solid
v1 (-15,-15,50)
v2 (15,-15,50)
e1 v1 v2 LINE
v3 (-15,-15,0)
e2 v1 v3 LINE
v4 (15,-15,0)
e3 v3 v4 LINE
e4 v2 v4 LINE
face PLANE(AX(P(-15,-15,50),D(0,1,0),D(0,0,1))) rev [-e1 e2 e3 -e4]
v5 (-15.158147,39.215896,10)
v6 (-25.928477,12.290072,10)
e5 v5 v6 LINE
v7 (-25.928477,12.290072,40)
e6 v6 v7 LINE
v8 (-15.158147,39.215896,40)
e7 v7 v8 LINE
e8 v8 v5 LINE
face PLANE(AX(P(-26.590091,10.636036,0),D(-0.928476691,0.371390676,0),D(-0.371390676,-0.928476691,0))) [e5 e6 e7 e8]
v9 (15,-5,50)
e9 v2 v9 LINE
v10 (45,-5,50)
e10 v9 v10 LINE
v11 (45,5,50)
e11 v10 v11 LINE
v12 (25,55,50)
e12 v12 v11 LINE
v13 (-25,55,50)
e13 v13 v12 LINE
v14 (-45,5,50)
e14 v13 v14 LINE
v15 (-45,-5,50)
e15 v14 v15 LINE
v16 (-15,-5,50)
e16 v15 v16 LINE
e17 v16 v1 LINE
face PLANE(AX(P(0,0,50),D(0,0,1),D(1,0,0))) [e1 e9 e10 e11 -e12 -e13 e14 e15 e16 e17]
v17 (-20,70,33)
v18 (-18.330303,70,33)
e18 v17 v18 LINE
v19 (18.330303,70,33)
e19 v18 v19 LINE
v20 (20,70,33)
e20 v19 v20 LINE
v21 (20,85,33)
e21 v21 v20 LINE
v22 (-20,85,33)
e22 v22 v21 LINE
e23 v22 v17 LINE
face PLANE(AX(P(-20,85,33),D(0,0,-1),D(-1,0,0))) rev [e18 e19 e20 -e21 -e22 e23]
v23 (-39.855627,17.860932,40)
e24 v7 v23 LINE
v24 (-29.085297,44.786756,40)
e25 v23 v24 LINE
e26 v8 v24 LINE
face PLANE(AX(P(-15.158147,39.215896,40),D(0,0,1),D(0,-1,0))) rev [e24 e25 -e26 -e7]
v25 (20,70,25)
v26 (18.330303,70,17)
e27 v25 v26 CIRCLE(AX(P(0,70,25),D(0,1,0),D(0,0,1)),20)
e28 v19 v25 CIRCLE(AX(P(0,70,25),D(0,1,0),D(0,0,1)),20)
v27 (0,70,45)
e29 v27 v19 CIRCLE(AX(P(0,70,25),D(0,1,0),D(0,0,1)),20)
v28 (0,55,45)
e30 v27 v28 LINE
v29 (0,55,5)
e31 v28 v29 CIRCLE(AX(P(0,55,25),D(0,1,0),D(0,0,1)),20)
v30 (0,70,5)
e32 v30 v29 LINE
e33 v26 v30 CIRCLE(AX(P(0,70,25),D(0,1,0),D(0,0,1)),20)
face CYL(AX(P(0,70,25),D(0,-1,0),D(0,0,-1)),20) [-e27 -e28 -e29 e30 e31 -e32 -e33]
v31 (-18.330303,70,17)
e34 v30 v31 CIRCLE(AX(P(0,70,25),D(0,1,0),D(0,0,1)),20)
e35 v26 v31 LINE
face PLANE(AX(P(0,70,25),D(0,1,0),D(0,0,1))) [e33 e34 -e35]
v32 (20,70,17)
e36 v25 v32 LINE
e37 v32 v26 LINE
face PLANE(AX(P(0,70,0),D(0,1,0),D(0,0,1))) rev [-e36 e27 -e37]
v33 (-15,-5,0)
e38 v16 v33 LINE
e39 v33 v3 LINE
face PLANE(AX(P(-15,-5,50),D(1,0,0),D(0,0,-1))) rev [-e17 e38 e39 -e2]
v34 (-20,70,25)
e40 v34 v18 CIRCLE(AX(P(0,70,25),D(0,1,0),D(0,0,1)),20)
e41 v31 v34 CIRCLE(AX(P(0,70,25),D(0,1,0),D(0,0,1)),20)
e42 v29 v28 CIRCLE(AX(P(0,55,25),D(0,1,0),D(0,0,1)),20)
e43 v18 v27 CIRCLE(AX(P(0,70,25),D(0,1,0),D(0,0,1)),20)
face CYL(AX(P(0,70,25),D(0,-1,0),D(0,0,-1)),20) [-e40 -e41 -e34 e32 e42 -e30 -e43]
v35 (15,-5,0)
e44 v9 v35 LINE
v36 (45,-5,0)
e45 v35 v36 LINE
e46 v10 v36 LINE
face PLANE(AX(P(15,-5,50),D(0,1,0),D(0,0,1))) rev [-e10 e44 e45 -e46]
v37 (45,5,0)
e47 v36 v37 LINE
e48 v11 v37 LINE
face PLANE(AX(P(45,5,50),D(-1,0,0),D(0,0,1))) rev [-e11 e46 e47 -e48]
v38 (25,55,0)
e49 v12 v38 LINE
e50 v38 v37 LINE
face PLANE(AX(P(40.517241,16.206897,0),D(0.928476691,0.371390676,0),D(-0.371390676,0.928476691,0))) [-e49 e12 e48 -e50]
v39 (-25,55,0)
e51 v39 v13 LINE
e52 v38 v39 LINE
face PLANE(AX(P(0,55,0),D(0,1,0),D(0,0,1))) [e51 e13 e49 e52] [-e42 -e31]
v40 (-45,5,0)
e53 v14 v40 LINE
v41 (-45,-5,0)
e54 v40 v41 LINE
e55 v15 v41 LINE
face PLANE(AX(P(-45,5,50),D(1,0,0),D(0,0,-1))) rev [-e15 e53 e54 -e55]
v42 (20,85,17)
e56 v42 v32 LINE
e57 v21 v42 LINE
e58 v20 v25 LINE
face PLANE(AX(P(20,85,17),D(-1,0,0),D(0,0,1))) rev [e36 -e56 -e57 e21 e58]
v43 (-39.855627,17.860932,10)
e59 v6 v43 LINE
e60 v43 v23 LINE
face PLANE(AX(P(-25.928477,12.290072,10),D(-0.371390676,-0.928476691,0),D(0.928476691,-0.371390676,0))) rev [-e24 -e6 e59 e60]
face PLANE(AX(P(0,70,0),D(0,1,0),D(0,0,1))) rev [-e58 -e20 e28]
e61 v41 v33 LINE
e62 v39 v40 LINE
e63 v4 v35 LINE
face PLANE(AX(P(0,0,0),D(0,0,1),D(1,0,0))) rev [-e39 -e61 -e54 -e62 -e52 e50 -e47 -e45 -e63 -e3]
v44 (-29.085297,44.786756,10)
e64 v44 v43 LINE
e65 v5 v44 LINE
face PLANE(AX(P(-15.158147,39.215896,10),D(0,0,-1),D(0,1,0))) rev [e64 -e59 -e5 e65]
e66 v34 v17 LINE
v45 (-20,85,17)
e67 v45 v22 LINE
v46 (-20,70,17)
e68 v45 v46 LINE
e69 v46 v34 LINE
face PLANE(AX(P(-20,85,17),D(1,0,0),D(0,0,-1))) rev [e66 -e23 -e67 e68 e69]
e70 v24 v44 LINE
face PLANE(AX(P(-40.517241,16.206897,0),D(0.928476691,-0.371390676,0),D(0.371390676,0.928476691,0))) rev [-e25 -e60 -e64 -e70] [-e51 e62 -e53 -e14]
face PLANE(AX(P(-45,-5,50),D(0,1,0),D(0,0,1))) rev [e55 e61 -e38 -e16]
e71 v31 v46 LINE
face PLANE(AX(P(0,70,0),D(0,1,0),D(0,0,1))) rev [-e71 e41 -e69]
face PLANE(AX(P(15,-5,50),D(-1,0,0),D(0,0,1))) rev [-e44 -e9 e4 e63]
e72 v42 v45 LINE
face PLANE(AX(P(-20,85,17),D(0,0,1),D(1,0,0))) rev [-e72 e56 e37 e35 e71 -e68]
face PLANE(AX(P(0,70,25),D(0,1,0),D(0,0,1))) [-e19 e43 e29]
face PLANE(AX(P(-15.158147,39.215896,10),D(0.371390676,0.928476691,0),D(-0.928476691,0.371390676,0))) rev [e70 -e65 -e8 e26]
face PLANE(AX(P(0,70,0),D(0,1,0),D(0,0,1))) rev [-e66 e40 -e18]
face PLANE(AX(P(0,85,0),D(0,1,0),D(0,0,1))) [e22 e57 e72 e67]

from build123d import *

# Parameters (mm, degrees)
BASE_BLOCK_DEPTH    = 50
ROUND_BOSS_SKETCH_R = 20
ROUND_BOSS_DEPTH    = 15
TOP_KEY_SKETCH_W    = 40
TOP_KEY_SKETCH_H    = 16
TOP_KEY_DEPTH       = 15
SLOT_SKETCH_W       = 30
SLOT_SKETCH_H       = 29
SLOT_CUT_DEPTH      = 15


with BuildPart() as part:
    # Base Profile Sketch → Base Block (new body)
    with BuildSketch(Plane.XY):
        Polygon((15, -5), (45, -5), (45, 5), (-45, 5), (-45, -5), (-15, -5), (-15, -15), (15, -15), align=None)
    extrude(amount=BASE_BLOCK_DEPTH)

    # Loft Top Profile Sketch → section 0 of tapered_body_loft
    with BuildSketch(Plane(origin=(0, 55, 0), x_dir=(1, 0, 0), z_dir=(0, 1, 0)), mode=Mode.PRIVATE) as tapered_body_loft_s0:
        with BuildLine():
            Line((-25, 0), (25, 0))
            Line((25, 0), (25, -50))
            Line((25, -50), (-25, -50))
            Line((-25, -50), (-25, 0))
        make_face()
    # loft up to a face of the part (tapered_body_loft)
    loft([tapered_body_loft_s0.sketch, part.faces().sort_by_distance((0, 5, 25))[0]])

    # Round Boss Sketch → Round Boss (add)
    with BuildSketch(Plane(origin=(0, 55, 0), x_dir=(1, 0, 0), z_dir=(0, 1, 0))):
        with Locations(Location((0, -25, 0), (0, 0, 270))):
            Circle(ROUND_BOSS_SKETCH_R)
    extrude(amount=ROUND_BOSS_DEPTH)

    # Top Key Sketch → Top Key (add)
    with BuildSketch(Plane(origin=(0, 70, 0), x_dir=(1, 0, 0), z_dir=(0, 1, 0))):
        with Locations((0, -25)):
            Rectangle(TOP_KEY_SKETCH_W, TOP_KEY_SKETCH_H)
    extrude(amount=TOP_KEY_DEPTH)

    # Slot Sketch → Slot Cut (cut)
    with BuildSketch(Plane(origin=(-40.517241379, 16.206896552, 0), x_dir=(0, 0, 1), z_dir=(-0.9284766908852594, 0.37139067635410355, 0))):
        with Locations((25, 16.28145109)):
            Rectangle(SLOT_SKETCH_W, SLOT_SKETCH_H)
    extrude(amount=-SLOT_CUT_DEPTH, mode=Mode.SUBTRACT)


solid = part.part
